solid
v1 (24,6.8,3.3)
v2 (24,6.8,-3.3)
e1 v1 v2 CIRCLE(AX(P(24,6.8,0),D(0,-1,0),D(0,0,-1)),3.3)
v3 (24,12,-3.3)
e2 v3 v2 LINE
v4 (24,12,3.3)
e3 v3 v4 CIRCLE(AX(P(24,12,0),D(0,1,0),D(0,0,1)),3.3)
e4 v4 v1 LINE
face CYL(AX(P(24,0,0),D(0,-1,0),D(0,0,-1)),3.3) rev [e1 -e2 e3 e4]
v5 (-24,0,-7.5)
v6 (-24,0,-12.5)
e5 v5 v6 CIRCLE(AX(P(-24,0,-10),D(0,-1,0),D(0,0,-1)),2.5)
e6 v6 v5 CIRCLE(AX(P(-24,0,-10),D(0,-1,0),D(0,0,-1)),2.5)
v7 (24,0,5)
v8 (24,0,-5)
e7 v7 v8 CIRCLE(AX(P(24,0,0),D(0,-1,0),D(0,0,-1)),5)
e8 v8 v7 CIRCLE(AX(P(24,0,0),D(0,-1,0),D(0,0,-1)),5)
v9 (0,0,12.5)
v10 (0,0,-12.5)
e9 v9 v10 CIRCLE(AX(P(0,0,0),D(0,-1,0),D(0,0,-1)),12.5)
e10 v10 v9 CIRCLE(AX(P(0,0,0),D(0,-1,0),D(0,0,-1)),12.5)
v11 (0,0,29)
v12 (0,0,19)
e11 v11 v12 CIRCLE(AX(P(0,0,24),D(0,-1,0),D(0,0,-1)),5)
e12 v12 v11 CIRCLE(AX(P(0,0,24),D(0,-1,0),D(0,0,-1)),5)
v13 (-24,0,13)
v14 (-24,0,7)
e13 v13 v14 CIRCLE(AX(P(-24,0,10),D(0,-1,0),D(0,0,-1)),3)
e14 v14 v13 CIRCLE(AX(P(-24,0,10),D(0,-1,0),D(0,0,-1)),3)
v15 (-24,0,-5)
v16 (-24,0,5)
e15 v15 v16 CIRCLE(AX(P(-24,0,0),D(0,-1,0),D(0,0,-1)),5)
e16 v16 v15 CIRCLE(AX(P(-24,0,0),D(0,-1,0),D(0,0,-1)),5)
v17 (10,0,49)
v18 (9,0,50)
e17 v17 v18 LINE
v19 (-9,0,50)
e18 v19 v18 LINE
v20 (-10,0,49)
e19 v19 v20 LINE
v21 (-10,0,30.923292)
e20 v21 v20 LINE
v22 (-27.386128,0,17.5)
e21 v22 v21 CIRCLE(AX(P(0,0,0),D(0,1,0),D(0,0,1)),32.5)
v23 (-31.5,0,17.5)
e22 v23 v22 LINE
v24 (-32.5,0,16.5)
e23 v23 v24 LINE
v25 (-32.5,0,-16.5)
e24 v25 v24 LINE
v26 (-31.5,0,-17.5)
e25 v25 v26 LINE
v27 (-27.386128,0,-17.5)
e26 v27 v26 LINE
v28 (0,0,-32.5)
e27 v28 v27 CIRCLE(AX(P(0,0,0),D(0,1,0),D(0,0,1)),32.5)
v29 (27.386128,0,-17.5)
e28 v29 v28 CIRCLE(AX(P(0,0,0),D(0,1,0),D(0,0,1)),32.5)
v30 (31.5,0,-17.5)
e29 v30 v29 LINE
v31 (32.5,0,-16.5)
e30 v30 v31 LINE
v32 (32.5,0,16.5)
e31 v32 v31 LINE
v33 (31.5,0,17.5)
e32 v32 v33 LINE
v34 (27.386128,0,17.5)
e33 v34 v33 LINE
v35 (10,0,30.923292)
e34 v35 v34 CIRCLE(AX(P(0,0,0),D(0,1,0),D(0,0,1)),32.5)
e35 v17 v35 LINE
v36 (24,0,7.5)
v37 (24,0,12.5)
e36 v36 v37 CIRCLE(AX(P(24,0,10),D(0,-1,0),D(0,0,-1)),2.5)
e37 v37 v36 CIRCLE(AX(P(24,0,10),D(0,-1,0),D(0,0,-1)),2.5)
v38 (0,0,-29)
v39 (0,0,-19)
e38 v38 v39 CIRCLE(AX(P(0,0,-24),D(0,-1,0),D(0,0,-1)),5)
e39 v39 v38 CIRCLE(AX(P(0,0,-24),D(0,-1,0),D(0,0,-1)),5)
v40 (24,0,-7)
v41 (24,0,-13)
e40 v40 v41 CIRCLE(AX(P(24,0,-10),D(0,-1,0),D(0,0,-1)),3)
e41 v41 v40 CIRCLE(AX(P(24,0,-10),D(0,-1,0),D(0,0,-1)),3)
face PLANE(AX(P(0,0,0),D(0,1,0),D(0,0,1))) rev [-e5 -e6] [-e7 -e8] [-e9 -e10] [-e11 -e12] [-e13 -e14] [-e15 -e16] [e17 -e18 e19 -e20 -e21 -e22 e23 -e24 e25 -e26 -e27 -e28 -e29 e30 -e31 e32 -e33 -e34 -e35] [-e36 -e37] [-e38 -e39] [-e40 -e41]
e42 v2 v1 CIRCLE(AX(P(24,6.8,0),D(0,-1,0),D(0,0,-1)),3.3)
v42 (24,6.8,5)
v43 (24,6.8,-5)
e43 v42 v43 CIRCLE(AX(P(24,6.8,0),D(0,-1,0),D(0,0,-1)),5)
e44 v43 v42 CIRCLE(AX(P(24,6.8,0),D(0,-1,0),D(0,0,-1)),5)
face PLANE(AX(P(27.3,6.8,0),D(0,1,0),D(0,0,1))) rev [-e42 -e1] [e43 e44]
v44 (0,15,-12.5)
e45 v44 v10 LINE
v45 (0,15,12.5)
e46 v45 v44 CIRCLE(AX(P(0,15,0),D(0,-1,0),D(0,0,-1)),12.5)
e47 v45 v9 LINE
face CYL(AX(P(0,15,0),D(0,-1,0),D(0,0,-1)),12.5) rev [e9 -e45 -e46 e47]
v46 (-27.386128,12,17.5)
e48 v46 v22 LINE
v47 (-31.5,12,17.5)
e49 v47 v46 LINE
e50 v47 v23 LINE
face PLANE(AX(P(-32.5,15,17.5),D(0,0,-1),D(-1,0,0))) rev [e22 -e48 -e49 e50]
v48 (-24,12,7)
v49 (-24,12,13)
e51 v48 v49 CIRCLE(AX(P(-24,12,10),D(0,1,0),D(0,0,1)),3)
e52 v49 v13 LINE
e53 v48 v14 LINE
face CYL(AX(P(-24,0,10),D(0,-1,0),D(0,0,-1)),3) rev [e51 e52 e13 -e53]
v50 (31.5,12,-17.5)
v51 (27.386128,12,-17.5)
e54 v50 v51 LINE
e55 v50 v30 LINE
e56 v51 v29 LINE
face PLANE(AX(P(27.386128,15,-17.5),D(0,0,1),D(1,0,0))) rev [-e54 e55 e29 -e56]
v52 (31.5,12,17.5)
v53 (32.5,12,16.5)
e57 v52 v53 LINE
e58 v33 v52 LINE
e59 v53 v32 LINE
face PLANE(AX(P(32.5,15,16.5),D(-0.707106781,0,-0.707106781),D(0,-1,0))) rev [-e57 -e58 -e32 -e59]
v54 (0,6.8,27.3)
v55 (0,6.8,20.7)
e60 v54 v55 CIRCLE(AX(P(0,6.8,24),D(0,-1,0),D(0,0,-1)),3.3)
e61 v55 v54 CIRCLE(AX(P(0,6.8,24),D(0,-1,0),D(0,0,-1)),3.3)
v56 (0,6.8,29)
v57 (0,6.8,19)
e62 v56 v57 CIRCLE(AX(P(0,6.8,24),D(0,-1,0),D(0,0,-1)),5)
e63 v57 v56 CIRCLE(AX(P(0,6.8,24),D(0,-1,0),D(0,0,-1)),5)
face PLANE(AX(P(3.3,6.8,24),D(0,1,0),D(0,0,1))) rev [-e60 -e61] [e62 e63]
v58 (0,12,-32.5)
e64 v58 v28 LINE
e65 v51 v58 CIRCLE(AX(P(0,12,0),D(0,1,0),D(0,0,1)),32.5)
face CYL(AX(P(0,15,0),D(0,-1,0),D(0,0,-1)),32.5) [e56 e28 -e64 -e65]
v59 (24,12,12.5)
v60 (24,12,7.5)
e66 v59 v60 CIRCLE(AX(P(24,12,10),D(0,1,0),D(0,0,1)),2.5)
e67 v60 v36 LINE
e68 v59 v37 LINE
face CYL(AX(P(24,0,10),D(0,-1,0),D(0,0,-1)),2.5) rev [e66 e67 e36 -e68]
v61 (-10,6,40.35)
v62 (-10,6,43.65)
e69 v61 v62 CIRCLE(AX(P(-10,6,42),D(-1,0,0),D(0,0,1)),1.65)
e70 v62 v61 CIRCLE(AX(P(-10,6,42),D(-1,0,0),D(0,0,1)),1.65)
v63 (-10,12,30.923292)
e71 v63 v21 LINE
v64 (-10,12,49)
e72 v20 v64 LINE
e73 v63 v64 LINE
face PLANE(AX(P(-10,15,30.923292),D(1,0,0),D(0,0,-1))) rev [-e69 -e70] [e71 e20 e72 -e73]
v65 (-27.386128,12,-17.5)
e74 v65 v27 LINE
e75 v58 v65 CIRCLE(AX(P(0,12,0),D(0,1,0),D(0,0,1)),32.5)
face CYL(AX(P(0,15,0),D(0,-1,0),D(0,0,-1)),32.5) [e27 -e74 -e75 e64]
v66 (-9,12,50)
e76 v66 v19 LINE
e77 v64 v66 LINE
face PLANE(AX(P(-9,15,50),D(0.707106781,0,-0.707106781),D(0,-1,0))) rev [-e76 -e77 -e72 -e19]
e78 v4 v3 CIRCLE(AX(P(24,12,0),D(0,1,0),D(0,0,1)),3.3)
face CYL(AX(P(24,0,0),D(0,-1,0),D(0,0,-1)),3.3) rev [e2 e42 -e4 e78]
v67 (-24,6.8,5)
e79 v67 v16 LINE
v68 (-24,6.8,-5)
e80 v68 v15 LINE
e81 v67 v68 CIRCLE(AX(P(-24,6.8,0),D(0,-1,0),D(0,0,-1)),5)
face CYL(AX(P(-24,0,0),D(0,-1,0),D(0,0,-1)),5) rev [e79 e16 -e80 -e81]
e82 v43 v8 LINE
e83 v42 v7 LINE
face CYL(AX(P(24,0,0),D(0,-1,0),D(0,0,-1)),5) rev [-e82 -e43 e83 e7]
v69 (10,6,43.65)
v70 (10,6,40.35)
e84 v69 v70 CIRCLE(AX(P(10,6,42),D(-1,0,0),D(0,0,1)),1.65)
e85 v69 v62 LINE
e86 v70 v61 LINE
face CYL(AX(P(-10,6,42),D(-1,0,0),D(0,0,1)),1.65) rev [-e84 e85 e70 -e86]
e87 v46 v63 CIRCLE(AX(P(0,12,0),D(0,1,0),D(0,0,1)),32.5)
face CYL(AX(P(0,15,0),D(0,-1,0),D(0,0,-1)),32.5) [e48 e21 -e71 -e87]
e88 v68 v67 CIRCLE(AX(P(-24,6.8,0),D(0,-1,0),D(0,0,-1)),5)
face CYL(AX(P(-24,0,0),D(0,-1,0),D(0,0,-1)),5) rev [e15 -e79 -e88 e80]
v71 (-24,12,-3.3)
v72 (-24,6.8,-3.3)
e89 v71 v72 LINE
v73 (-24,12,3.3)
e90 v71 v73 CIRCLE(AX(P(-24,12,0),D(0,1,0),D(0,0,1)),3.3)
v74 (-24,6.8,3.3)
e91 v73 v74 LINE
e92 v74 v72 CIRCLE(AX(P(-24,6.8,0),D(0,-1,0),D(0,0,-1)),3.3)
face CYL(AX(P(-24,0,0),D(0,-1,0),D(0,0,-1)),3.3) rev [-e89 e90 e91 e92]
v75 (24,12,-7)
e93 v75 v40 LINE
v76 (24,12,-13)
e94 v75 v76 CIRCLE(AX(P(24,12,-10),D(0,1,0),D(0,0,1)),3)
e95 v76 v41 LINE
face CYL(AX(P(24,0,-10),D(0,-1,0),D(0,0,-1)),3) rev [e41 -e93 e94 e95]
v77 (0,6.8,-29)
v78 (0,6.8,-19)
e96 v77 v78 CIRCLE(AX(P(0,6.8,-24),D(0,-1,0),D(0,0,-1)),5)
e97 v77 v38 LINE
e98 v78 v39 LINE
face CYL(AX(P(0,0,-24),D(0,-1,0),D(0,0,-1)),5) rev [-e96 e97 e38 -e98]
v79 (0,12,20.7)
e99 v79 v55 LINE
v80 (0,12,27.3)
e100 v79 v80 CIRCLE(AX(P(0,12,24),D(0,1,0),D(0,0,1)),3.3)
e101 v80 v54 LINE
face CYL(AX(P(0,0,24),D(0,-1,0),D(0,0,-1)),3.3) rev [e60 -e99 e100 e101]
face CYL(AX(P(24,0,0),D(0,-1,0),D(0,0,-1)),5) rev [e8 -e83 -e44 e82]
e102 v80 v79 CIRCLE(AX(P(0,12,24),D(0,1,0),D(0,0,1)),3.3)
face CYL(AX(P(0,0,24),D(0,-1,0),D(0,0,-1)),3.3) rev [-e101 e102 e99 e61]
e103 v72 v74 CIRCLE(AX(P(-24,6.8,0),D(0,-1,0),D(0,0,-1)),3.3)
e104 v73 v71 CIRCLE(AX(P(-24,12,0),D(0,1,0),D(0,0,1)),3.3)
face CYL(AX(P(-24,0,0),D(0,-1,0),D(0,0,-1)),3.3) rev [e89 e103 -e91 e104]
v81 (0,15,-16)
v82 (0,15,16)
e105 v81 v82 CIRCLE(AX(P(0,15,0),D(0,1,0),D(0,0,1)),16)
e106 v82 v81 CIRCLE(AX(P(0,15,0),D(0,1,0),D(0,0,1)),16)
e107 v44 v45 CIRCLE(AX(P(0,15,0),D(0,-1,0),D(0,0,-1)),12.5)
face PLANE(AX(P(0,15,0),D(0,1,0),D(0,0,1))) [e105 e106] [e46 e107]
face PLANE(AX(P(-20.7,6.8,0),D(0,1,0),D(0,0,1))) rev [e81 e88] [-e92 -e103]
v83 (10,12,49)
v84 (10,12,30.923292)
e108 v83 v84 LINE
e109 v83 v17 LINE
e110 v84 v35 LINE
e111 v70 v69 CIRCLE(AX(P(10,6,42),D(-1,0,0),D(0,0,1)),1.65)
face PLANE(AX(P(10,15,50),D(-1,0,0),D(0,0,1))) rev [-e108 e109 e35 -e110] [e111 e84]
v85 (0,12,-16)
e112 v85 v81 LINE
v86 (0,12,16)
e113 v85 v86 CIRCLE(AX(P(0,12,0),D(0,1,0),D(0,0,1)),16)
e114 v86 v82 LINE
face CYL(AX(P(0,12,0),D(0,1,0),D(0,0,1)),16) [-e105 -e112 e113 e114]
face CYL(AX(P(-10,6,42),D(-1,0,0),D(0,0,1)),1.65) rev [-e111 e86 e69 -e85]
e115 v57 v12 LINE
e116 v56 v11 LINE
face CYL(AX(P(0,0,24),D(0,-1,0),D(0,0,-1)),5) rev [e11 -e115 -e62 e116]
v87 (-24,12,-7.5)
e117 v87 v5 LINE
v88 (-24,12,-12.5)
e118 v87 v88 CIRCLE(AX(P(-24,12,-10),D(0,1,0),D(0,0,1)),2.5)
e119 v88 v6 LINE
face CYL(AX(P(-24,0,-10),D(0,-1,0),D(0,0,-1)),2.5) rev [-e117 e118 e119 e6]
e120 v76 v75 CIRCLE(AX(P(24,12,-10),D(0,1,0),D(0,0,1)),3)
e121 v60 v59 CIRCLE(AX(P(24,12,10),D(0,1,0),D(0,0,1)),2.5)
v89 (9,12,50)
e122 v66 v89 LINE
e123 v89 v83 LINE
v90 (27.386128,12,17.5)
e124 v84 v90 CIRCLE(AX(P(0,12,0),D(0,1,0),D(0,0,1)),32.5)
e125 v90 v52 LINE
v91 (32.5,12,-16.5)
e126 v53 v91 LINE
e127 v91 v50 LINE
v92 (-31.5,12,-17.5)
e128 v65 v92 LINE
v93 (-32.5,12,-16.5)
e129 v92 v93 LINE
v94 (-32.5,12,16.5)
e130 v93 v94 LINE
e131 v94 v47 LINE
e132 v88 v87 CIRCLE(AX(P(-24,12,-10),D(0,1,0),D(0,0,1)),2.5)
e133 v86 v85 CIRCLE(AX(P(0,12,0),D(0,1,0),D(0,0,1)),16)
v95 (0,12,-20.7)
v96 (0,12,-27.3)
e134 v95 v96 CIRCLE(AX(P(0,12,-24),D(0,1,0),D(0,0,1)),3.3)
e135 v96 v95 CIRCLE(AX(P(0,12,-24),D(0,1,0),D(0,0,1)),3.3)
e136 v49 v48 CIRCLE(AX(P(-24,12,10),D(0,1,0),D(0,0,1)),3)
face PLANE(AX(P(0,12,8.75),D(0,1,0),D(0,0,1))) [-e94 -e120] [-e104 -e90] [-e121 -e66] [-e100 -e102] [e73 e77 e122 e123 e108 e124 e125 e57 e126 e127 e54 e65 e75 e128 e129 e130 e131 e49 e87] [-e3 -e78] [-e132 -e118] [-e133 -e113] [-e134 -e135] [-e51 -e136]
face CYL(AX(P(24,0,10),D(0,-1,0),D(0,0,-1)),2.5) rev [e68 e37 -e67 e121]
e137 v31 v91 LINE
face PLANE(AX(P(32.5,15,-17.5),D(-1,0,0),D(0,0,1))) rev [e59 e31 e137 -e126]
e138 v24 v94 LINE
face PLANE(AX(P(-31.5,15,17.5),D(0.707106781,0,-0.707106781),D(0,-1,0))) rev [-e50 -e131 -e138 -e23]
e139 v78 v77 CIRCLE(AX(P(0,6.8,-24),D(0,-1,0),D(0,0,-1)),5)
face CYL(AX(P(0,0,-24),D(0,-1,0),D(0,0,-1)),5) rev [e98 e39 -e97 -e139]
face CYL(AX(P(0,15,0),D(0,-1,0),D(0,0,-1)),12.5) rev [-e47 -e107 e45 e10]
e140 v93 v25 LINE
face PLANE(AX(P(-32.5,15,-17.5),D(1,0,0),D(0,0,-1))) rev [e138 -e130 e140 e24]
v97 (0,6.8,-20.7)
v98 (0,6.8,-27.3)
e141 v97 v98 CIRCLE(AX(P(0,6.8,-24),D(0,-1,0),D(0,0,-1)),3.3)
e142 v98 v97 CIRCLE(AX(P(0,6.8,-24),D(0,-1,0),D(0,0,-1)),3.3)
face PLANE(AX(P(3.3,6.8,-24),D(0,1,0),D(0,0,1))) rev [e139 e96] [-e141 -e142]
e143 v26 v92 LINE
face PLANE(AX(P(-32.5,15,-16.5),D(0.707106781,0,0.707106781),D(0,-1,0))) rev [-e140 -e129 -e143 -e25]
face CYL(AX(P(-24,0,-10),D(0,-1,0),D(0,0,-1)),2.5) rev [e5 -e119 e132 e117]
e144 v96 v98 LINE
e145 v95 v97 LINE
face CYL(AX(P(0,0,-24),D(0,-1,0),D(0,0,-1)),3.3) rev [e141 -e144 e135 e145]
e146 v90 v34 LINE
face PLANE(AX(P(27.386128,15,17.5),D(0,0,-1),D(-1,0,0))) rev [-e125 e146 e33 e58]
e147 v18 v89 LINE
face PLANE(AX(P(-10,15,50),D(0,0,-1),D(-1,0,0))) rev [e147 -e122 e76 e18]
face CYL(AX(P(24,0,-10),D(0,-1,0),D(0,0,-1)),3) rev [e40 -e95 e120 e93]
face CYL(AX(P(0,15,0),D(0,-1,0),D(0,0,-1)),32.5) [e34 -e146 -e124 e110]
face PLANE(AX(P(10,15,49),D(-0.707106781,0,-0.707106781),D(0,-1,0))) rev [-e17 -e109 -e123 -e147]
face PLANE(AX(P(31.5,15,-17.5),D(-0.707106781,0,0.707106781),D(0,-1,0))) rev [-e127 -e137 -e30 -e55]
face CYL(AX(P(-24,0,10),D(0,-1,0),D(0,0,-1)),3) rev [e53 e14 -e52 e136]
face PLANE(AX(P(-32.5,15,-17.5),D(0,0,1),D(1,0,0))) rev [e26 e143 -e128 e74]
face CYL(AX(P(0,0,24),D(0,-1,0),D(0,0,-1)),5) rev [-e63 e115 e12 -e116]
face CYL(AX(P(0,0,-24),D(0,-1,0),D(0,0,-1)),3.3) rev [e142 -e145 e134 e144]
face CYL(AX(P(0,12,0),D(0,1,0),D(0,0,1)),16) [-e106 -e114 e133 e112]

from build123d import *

# Parameters (mm, degrees)
EXTRUDE_1_DEPTH              = 15
SKETCH_2_OUTSIDE_W           = 88.22
SKETCH_2_OUTSIDE_H           = 105.72
SKETCH_2_OUTSIDE_R           = 16
CUT_EXTRUDE_1_DEPTH          = 3
SKETCH_3_R                   = 12.5
CUT_EXTRUDE_2_DEPTH          = 62.491869381
HOLE_WIZARD_M6_1_D           = 6.6
HOLE_WIZARD_M6_1_CBORE_D     = 10
HOLE_WIZARD_M6_1_CBORE_DEPTH = 6.8
F_6_0MM_1_D                  = 6
HOLE_WIZARD_M4_1_D           = 3.3
HOLE_WIZARD_M6_2_D           = 5
CHAMFER_1_SIZE               = 1


with BuildPart() as part:
    # 草图1 → 凸台-拉伸1 (new body)
    with BuildSketch(Plane(origin=(0, 0, 0), x_dir=(1, 0, 0), z_dir=(0, 1, 0))):
        with BuildLine():
            Line((-10, -30.923292192), (-10, -50))
            Line((-10, -50), (10, -50))
            Line((10, -50), (10, -30.923292192))
            ThreePointArc((10, -30.923292192), (19.861440851, -25.724952231), (27.386127875, -17.5))
            Line((27.386127875, -17.5), (32.5, -17.5))
            Line((32.5, -17.5), (32.5, 17.5))
            Line((32.5, 17.5), (27.386127875, 17.5))
            ThreePointArc((27.386127875, 17.5), (0, 32.5), (-27.386127875, 17.5))
            Line((-27.386127875, 17.5), (-32.5, 17.5))
            Line((-32.5, 17.5), (-32.5, -17.5))
            Line((-32.5, -17.5), (-27.386127875, -17.5))
            ThreePointArc((-27.386127875, -17.5), (-19.861440851, -25.724952231), (-10, -30.923292192))
        make_face()
    extrude(amount=EXTRUDE_1_DEPTH)

    # 草图2 outside → 切除-拉伸1 (cut)
    with BuildSketch(Plane(origin=(0, 15, 0), x_dir=(1, 0, 0), z_dir=(0, 1, 0))):
        with Locations((0, -8.75)):
            Rectangle(SKETCH_2_OUTSIDE_W, SKETCH_2_OUTSIDE_H)
        with Locations(Location((0, 0, 0), (0, 0, 270))):
            Circle(SKETCH_2_OUTSIDE_R, mode=Mode.SUBTRACT)
    extrude(amount=-CUT_EXTRUDE_1_DEPTH, mode=Mode.SUBTRACT)

    # 草图3 → 切除-拉伸2 (cut, through all)
    with BuildSketch(Plane.XZ):
        with Locations(Location((0, 0, 0), (0, 0, 270))):
            Circle(SKETCH_3_R)
    extrude(amount=-CUT_EXTRUDE_2_DEPTH, mode=Mode.SUBTRACT)

    # M6 六角圆柱头螺钉的柱形沉头孔1 (through all)
    with Locations(Plane(origin=(0, 0, 0), x_dir=(-1, 0, 0), z_dir=(0, -1, 0))):
        with Locations((0, 24), (24, 0), (0, -24), (-24, 0)):
            CounterBoreHole(HOLE_WIZARD_M6_1_D / 2, HOLE_WIZARD_M6_1_CBORE_D / 2, HOLE_WIZARD_M6_1_CBORE_DEPTH)

    # Ø6.0mm 暗销孔1 (through all)
    with Locations(Plane(origin=(0, 0, 0), x_dir=(-1, 0, 0), z_dir=(0, -1, 0))):
        with Locations((-24, 10), (24, -10)):
            Hole(F_6_0MM_1_D / 2)

    # M4 螺纹孔1 (through all)
    with Locations(Plane.ZY.offset(10)):
        with Locations((42, 6)):
            Hole(HOLE_WIZARD_M4_1_D / 2)

    # M6 螺纹孔2 (through all)
    with Locations(Plane(origin=(0, 0, 0), x_dir=(-1, 0, 0), z_dir=(0, -1, 0))):
        with Locations((24, 10), (-24, -10)):
            Hole(HOLE_WIZARD_M6_2_D / 2)

    # 倒角1
    chamfer_1_edges = [part.edges().sort_by_distance(p)[0] for p in [
        (10, 6, 50),
        (-10, 6, 50),
        (-32.5, 6, 17.5),
        (-32.5, 6, -17.5),
        (32.5, 6, -17.5),
        (32.5, 6, 17.5),
    ]]
    chamfer(chamfer_1_edges, length=CHAMFER_1_SIZE)


solid = part.part
